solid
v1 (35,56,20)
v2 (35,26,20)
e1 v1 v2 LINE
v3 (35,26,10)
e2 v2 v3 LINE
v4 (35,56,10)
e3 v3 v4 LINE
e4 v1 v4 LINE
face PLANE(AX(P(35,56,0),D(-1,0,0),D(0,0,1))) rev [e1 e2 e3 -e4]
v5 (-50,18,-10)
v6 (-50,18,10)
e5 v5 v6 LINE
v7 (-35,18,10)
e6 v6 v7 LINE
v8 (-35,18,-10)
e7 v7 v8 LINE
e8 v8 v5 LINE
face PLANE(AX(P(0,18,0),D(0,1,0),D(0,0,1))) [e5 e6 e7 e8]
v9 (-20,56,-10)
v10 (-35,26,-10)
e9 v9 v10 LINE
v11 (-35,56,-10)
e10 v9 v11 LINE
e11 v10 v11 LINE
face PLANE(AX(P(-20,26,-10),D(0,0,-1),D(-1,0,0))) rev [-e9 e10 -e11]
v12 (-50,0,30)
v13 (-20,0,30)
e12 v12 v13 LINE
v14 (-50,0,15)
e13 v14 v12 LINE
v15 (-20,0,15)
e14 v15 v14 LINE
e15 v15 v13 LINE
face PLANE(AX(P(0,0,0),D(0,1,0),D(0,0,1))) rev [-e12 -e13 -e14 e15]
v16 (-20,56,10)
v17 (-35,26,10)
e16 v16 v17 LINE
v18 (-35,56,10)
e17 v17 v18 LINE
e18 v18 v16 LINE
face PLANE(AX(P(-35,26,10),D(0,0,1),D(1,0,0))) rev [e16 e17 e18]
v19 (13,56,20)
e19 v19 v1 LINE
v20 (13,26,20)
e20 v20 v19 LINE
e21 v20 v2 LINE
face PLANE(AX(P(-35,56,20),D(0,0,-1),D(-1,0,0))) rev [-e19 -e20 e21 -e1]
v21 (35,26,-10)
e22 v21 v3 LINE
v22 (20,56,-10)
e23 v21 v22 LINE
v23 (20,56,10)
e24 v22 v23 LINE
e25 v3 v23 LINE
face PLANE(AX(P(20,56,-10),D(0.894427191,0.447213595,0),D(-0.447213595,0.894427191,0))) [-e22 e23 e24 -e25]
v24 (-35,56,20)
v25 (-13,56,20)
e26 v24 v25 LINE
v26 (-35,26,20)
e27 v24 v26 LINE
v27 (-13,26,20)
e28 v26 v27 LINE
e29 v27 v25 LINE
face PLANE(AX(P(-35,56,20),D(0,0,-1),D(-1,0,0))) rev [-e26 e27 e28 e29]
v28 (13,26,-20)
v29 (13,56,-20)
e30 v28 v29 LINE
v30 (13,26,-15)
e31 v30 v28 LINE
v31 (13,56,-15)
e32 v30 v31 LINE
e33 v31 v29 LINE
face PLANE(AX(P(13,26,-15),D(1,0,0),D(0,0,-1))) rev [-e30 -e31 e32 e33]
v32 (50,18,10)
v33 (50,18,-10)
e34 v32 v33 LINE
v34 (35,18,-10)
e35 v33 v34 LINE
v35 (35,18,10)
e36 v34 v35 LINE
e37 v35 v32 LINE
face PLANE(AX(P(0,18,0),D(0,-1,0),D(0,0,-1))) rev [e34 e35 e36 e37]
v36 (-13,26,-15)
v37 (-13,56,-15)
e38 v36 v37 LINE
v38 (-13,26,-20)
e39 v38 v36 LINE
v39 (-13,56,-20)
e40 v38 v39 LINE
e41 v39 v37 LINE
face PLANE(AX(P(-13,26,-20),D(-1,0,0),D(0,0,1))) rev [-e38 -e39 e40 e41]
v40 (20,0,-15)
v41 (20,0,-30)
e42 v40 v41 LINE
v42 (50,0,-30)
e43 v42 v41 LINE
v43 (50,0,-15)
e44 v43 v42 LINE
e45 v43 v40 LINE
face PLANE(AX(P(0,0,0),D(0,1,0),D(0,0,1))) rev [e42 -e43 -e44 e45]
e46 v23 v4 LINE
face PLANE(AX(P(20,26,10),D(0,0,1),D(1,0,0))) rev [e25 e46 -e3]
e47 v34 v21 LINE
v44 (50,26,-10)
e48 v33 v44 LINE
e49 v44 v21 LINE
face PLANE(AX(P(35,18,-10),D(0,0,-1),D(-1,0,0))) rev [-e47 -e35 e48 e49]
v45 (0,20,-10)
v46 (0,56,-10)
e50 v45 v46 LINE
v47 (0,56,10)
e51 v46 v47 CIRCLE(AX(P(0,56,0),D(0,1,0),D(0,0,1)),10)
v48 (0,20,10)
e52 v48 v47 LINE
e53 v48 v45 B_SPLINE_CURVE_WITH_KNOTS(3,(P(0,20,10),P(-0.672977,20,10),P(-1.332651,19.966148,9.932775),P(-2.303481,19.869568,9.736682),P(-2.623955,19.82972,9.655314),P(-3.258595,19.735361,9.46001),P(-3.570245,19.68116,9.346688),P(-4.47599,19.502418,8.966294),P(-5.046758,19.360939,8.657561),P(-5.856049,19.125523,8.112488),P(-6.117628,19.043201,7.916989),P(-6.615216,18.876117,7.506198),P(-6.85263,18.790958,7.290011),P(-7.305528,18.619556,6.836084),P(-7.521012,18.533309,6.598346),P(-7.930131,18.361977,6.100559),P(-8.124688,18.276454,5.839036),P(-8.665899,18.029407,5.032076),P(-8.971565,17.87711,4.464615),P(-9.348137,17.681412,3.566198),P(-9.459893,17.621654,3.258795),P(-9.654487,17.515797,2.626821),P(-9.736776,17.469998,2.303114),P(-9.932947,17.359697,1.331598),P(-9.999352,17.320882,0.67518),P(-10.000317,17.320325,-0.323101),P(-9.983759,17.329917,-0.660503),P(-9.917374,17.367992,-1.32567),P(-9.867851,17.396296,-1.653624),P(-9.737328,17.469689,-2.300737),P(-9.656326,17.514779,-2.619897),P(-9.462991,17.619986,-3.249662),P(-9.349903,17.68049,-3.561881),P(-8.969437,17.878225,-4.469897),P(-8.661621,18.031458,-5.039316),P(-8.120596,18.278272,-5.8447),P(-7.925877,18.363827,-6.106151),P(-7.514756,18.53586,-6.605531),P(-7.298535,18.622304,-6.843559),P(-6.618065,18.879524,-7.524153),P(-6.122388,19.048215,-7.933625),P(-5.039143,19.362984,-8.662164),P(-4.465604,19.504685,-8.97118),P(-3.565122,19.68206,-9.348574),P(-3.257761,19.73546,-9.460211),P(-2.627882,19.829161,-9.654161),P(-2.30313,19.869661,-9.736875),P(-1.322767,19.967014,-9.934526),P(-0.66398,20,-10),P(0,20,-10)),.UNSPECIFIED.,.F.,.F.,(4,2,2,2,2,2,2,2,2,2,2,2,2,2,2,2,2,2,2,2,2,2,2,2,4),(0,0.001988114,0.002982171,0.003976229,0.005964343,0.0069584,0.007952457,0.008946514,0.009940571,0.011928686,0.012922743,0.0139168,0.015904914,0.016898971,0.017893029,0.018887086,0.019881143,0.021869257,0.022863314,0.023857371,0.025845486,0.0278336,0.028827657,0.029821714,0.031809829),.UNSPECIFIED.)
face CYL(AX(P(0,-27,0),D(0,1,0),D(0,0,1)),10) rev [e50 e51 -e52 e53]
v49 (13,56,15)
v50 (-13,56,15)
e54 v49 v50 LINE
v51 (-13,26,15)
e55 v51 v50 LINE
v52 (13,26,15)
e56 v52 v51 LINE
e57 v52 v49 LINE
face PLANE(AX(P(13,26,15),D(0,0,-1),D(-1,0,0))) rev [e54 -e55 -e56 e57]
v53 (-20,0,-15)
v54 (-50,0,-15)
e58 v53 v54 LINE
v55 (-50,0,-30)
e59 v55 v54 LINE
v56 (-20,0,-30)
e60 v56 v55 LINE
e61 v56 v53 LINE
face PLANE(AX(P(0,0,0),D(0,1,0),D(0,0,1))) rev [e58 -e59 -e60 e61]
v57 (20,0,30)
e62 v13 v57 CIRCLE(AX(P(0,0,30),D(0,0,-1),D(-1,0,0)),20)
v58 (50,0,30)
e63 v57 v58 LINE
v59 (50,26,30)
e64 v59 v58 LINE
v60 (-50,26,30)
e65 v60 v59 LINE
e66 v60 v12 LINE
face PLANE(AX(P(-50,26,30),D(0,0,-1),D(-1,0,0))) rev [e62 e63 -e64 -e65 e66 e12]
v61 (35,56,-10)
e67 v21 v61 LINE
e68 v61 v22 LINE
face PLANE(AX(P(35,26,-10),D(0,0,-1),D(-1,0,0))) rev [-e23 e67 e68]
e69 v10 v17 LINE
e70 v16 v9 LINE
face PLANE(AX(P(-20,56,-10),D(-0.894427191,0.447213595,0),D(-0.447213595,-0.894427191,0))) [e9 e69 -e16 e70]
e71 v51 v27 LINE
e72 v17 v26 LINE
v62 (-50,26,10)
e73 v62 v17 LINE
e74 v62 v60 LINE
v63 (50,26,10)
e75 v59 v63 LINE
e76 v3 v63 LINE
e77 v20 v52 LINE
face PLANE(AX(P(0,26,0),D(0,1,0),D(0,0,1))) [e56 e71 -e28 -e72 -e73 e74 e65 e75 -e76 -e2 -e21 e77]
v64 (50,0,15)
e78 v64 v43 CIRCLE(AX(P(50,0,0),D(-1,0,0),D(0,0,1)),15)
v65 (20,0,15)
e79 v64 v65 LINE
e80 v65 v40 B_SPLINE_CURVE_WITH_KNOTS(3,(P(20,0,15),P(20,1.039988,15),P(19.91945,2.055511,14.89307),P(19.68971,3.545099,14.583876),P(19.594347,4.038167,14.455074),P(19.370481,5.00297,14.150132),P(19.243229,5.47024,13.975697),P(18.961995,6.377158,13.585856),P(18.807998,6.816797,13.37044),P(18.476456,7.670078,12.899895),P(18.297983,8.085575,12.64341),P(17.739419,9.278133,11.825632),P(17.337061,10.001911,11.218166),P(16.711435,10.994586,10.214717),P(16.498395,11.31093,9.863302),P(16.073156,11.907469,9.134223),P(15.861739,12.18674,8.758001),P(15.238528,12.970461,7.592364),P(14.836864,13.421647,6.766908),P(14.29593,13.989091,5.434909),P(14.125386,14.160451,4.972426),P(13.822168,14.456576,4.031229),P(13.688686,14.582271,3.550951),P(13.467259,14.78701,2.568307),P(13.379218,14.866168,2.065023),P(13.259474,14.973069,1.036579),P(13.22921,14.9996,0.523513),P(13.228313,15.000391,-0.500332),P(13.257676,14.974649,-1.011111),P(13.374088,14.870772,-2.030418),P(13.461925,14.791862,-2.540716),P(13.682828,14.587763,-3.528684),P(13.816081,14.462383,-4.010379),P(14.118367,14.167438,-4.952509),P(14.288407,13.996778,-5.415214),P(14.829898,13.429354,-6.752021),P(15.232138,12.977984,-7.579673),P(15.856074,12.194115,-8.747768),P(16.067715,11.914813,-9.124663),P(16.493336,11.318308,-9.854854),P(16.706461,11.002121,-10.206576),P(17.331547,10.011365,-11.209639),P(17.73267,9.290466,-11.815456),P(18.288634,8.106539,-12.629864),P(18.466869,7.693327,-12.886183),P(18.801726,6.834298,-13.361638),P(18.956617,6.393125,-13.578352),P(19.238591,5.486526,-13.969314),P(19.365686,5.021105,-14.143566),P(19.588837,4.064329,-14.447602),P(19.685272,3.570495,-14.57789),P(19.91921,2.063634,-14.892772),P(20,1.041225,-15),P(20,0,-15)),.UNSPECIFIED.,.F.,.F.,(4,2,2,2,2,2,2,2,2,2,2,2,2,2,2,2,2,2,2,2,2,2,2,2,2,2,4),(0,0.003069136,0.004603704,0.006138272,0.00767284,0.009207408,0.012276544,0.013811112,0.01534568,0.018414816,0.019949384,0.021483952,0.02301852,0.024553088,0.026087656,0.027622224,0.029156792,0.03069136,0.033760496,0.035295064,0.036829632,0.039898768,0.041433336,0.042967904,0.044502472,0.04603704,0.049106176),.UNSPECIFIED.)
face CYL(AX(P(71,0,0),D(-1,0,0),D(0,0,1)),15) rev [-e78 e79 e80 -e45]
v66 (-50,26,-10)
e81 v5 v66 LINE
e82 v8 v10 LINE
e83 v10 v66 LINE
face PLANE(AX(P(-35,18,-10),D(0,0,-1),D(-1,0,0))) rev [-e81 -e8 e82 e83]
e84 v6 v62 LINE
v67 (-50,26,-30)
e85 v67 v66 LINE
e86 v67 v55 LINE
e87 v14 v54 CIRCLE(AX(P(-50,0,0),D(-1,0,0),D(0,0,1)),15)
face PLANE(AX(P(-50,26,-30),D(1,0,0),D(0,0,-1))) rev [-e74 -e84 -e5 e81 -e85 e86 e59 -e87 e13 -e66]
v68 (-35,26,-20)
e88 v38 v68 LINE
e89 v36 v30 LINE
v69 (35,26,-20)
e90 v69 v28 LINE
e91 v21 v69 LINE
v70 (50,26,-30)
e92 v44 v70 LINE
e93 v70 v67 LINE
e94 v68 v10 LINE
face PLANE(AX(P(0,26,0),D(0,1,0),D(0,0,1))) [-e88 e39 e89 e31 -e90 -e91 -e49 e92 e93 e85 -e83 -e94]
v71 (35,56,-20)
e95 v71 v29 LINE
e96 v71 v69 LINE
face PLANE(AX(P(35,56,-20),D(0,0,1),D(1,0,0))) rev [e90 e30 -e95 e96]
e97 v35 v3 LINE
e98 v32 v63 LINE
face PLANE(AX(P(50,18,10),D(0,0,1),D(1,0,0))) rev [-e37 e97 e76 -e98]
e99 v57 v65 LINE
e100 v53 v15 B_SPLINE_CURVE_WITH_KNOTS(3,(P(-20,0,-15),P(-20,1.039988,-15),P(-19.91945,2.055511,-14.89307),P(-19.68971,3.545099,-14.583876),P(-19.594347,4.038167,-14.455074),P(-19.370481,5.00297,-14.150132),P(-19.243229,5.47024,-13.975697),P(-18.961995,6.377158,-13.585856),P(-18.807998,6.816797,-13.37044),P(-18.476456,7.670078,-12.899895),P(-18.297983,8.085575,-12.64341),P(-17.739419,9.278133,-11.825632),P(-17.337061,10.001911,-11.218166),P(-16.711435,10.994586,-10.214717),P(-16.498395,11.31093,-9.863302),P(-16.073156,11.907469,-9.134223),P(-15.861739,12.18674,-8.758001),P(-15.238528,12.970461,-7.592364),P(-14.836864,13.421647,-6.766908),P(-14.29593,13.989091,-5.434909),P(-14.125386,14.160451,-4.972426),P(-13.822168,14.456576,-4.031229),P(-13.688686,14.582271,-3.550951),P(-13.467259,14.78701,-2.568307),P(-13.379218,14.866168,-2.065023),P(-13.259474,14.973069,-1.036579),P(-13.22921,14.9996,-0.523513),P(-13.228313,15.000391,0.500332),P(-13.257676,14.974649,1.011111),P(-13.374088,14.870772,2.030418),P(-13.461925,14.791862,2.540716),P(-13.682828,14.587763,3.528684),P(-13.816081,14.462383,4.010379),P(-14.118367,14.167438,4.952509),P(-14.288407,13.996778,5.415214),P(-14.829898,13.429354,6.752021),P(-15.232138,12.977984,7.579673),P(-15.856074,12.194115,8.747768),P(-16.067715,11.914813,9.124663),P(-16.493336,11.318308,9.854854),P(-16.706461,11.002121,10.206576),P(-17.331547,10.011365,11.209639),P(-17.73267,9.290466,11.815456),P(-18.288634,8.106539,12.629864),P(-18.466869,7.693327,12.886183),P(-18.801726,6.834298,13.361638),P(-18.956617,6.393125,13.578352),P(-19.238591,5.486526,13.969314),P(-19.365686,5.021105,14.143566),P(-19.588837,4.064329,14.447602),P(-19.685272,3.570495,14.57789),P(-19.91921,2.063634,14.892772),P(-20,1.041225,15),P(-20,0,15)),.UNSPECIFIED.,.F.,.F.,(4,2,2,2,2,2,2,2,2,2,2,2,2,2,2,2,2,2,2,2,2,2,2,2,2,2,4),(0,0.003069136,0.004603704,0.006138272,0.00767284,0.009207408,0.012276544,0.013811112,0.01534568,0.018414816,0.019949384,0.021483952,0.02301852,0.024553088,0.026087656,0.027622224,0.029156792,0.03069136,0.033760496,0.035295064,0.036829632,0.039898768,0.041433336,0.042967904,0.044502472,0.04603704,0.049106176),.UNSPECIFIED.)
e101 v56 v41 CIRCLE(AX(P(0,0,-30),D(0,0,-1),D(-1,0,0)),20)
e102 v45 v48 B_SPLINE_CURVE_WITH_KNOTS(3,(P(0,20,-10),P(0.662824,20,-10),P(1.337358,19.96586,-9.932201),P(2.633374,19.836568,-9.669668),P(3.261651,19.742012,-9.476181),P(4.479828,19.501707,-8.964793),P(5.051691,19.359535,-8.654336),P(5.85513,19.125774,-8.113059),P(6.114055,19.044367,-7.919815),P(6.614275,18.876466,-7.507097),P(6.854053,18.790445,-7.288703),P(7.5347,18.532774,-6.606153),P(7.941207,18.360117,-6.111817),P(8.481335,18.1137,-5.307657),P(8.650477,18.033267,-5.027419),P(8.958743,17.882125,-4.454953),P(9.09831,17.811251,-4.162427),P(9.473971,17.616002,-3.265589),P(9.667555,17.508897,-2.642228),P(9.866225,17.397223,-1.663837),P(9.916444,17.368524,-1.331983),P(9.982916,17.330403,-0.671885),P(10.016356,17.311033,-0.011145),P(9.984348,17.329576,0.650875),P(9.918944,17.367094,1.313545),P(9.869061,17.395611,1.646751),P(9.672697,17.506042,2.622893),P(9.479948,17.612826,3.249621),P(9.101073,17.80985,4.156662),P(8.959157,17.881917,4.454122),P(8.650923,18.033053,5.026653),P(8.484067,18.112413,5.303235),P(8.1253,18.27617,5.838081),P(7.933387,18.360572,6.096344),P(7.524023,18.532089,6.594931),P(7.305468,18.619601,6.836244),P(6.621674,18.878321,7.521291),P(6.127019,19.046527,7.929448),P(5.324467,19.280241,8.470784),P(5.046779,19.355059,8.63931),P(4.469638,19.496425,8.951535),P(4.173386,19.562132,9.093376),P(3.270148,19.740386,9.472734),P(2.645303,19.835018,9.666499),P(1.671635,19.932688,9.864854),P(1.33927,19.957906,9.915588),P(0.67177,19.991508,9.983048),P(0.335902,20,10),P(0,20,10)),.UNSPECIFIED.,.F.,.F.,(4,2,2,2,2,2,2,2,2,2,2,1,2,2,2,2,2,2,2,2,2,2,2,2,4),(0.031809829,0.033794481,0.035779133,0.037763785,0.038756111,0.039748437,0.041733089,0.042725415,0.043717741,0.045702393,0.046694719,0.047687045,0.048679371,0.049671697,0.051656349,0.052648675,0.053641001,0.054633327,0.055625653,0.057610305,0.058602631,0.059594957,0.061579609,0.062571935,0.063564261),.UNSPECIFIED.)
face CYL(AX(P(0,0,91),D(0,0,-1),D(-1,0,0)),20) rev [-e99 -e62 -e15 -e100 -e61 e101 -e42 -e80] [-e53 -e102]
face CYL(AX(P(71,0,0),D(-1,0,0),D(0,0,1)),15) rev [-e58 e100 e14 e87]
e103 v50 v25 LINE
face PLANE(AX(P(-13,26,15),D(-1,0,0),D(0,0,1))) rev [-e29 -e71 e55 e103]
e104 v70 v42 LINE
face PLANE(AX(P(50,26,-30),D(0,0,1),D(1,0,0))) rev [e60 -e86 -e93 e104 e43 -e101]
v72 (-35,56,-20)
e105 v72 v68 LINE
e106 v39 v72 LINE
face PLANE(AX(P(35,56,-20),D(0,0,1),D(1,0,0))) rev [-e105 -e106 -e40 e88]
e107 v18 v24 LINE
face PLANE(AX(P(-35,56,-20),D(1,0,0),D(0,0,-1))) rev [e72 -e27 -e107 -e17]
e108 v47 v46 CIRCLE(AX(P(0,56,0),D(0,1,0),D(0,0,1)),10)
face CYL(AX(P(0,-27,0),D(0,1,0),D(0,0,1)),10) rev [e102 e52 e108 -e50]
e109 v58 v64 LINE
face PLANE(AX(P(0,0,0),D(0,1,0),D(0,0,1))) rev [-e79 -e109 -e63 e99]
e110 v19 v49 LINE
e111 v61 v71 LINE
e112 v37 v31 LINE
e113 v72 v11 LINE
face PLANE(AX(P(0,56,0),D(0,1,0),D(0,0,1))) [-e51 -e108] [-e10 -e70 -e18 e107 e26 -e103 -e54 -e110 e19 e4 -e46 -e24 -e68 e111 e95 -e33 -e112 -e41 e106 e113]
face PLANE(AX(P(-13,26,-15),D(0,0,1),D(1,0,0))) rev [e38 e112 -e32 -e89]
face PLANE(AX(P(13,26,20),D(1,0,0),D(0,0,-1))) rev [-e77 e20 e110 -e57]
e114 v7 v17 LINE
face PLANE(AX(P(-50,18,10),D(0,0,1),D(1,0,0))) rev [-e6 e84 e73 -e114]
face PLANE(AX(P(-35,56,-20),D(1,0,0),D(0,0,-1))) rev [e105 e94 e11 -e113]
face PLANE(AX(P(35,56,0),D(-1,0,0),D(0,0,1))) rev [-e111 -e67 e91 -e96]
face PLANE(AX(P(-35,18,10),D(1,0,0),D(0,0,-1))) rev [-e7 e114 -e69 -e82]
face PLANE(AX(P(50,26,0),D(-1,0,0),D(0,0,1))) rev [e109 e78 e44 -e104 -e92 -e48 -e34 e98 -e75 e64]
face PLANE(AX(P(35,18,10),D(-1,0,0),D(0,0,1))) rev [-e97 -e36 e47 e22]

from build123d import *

# Parameters (mm, degrees)
BASE_BLOCK_DEPTH        = 26
UPPER_GUIDE_BLOCK_DEPTH = 30
GUIDE_SLOTS_SKETCH_W    = 26
GUIDE_SLOTS_SKETCH_H    = 5
GUIDE_SLOTS_SKETCH_W_2  = 15
GUIDE_SLOTS_SKETCH_H_2  = 20
GUIDE_SLOTS_CUT_DEPTH   = 30
OFFSET_BOSS_DEPTH       = 20
TOP_BORE_SKETCH_R       = 10
TOP_BORE_DEPTH          = 83
POCKET_SKETCH_W         = 15
POCKET_SKETCH_H         = 20
POCKET_8MM_DEEP_DEPTH   = 8
SIDE_ARCH_CUT_DEPTH     = 121
BEARING_ARCH_SKETCH_R   = 20
BEARING_ARCH_CUT_DEPTH  = 121


with BuildPart() as part:
    # Base Profile Sketch → Base Block (new body)
    with BuildSketch(Plane(origin=(0, 0, 0), x_dir=(1, 0, 0), z_dir=(0, 1, 0))):
        Polygon((50, 0), (50, 30), (-50, 30), (-50, -30), (50, -30), align=None)
    extrude(amount=BASE_BLOCK_DEPTH)

    # Upper Block Sketch → Upper Guide Block (add)
    with BuildSketch(Plane(origin=(0, 26, 0), x_dir=(1, 0, 0), z_dir=(0, 1, 0))):
        Polygon((35, 0), (35, 20), (-35, 20), (-35, -20), (35, -20), align=None)
    extrude(amount=UPPER_GUIDE_BLOCK_DEPTH)

    # Guide Slots Sketch → Guide Slots Cut (cut)
    with BuildSketch(Plane(origin=(0, 56, 0), x_dir=(1, 0, 0), z_dir=(0, 1, 0))):
        Polygon((35, 0), (35, 10), (20, 10), (20, -10), (35, -10), align=None)
        with Locations((0, -17.5)):
            Rectangle(GUIDE_SLOTS_SKETCH_W, GUIDE_SLOTS_SKETCH_H)
        with Locations((-27.5, 0)):
            Rectangle(GUIDE_SLOTS_SKETCH_W_2, GUIDE_SLOTS_SKETCH_H_2)
        with Locations((0, 17.5)):
            Rectangle(GUIDE_SLOTS_SKETCH_W, GUIDE_SLOTS_SKETCH_H)
    extrude(amount=-GUIDE_SLOTS_CUT_DEPTH, mode=Mode.SUBTRACT)

    # Offset Boss Sketch → Offset Boss (add)
    with BuildSketch(Plane.XY.offset(10)):
        Polygon((-20, 56), (-35, 26), (-20, 26), align=None)
        Polygon((20, 56), (35, 26), (20, 26), align=None)
    extrude(amount=-OFFSET_BOSS_DEPTH)

    # Top Bore Sketch → Top Bore (cut)
    with BuildSketch(Plane(origin=(0, 56, 0), x_dir=(1, 0, 0), z_dir=(0, 1, 0))):
        with Locations(Location((0, 0, 0), (0, 0, 270))):
            Circle(TOP_BORE_SKETCH_R)
    extrude(amount=-TOP_BORE_DEPTH, mode=Mode.SUBTRACT)

    # Pocket Sketch → Pocket 8mm Deep (cut)
    with BuildSketch(Plane(origin=(0, 26, 0), x_dir=(1, 0, 0), z_dir=(0, 1, 0))):
        with Locations((42.5, 0)):
            Rectangle(POCKET_SKETCH_W, POCKET_SKETCH_H)
        with Locations((-42.5, 0)):
            Rectangle(POCKET_SKETCH_W, POCKET_SKETCH_H)
    extrude(amount=-POCKET_8MM_DEEP_DEPTH, mode=Mode.SUBTRACT)

    # Side Arch Sketch → Side Arch Cut (cut)
    with BuildSketch(Plane.ZY.offset(50)):
        with BuildLine():
            Line((-15, 0), (15, 0))
            ThreePointArc((15, 0), (0, 15), (-15, 0))
        make_face()
    extrude(amount=-SIDE_ARCH_CUT_DEPTH, mode=Mode.SUBTRACT)

    # Bearing Arch Sketch → Bearing Arch Cut (cut)
    with BuildSketch(Plane(origin=(0, 0, -30), x_dir=(-1, 0, 0), z_dir=(0, 0, -1))):
        Circle(BEARING_ARCH_SKETCH_R)
    extrude(amount=-BEARING_ARCH_CUT_DEPTH, mode=Mode.SUBTRACT)


solid = part.part
